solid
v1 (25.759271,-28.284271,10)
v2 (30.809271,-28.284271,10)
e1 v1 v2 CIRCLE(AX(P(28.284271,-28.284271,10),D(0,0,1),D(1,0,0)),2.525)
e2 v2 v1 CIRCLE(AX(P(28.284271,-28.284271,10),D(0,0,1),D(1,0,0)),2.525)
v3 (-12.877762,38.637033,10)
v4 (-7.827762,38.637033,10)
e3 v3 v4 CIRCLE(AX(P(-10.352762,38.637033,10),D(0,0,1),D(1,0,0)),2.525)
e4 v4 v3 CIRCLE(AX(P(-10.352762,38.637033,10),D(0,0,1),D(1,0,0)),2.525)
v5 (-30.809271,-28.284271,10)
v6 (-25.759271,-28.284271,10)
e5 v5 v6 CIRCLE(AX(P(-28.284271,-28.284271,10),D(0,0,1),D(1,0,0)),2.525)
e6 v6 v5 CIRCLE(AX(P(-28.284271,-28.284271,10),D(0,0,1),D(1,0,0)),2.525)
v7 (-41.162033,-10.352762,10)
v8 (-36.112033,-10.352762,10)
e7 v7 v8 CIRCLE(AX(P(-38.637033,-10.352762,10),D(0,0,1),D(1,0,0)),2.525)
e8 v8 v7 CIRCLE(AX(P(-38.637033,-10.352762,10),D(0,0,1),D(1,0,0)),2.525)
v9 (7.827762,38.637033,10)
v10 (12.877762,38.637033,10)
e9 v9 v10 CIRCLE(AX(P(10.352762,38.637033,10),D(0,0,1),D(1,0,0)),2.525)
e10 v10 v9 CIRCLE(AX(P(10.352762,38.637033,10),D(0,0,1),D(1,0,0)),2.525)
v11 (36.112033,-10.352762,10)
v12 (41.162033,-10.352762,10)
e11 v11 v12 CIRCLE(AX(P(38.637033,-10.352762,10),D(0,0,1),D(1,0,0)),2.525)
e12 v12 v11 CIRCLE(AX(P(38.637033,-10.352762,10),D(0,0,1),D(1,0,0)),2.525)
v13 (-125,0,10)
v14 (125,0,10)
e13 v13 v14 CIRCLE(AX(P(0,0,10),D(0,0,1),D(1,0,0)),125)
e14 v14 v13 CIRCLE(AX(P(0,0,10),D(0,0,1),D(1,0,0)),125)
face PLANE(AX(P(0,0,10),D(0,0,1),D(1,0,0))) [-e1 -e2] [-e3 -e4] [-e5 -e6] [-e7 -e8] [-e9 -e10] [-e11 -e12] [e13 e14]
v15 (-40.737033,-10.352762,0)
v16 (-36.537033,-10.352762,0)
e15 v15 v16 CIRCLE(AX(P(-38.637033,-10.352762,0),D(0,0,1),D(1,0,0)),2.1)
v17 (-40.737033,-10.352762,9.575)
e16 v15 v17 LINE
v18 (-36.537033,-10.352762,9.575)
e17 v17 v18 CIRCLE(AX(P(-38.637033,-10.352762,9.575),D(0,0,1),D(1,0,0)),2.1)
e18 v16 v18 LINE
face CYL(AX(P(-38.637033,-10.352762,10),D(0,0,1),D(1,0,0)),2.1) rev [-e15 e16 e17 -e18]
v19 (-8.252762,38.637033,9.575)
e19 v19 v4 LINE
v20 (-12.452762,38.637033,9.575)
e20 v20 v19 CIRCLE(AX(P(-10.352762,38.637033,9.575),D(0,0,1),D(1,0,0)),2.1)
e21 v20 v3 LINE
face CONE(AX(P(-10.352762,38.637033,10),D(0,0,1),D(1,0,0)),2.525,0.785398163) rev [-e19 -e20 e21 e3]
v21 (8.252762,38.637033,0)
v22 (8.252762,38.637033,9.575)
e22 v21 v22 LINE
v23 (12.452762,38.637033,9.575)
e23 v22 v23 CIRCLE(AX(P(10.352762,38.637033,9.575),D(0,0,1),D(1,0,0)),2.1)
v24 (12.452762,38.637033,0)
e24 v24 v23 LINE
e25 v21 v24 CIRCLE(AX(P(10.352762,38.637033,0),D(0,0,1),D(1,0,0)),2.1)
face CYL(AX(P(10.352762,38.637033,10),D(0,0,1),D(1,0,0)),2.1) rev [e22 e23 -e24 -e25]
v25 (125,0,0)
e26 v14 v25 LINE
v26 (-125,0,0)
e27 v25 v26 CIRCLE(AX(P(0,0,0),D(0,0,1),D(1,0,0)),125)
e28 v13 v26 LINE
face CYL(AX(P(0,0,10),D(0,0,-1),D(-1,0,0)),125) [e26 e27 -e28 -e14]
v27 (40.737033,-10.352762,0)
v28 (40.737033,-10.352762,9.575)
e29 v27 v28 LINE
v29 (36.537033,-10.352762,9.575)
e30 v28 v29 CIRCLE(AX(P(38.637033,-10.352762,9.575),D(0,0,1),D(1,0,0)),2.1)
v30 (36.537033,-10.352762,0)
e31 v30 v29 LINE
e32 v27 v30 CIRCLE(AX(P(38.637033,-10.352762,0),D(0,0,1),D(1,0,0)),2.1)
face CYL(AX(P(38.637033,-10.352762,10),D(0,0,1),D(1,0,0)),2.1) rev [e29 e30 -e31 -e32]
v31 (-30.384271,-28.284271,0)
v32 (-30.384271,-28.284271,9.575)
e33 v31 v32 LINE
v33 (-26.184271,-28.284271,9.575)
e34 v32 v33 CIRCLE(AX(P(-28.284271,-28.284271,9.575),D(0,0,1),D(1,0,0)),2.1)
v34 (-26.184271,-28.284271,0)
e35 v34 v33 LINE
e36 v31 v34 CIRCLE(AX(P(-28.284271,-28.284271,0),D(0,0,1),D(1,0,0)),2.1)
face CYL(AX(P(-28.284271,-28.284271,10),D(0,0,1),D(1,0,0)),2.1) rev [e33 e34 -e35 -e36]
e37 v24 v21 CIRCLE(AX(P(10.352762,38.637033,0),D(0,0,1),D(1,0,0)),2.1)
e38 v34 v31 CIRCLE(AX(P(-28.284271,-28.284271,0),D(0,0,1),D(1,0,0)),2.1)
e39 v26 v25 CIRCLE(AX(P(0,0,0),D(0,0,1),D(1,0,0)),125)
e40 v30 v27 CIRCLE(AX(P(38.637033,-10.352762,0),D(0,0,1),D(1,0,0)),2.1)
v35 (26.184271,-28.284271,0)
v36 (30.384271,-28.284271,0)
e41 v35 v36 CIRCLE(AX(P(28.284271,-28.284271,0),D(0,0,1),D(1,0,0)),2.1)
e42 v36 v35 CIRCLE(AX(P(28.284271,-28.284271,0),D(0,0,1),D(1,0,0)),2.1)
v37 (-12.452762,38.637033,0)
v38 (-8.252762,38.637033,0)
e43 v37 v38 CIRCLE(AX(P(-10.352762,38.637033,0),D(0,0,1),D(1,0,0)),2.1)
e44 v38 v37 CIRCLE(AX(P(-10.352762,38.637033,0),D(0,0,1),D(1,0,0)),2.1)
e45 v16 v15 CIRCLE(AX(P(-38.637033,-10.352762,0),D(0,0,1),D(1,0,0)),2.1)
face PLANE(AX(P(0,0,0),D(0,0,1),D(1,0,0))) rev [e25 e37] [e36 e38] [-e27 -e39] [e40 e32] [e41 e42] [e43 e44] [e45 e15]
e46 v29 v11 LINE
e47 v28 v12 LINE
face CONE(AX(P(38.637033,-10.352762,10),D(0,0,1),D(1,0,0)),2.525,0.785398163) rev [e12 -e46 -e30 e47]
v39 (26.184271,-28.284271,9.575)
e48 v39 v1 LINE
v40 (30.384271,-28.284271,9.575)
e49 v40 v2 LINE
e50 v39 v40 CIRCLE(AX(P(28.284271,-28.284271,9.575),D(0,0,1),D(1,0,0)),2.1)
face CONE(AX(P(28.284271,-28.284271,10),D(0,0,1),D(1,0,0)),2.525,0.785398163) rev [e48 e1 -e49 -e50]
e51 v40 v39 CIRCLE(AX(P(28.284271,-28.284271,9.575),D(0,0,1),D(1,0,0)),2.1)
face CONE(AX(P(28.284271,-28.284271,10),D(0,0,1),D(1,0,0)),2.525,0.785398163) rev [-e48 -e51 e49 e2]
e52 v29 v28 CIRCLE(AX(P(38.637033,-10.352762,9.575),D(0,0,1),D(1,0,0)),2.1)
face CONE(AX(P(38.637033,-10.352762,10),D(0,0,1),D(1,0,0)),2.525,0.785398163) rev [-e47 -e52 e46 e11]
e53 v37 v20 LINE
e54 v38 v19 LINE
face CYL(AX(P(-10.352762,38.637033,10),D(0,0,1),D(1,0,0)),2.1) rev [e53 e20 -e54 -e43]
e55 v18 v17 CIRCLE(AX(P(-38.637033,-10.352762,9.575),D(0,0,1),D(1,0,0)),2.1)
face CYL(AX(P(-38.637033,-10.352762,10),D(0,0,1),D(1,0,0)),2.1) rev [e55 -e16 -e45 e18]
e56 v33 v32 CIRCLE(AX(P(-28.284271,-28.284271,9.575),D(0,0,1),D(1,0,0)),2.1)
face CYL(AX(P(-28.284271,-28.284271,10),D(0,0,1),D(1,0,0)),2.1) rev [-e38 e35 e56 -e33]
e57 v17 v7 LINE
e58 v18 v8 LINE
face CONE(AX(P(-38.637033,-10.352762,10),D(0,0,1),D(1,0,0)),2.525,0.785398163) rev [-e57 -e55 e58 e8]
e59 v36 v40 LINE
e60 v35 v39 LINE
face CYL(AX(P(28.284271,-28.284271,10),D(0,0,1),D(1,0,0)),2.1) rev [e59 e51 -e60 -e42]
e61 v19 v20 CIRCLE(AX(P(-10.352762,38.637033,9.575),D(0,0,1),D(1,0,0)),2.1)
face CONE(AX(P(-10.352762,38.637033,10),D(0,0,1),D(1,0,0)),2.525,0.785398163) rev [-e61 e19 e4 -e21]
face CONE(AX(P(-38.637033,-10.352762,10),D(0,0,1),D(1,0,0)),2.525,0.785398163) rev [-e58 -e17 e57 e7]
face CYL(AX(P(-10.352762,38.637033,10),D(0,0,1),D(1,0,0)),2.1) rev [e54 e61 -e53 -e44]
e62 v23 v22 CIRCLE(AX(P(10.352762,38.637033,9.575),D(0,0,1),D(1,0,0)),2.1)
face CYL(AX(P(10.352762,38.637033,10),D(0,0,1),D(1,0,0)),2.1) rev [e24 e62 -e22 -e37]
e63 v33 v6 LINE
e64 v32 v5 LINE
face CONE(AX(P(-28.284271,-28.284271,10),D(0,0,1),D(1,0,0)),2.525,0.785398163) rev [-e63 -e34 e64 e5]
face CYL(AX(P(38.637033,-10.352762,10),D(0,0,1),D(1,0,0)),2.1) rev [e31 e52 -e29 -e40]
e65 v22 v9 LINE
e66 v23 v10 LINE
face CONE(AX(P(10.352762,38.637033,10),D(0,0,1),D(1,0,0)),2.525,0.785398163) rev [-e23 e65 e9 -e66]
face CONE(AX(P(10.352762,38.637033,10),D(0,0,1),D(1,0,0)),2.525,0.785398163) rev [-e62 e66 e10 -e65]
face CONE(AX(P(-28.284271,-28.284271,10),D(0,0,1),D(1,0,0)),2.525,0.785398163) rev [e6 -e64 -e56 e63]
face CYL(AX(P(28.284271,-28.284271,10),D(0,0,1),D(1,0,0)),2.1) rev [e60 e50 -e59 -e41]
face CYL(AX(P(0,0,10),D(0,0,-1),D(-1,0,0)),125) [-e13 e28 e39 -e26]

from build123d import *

# Parameters (mm, degrees)
SKETCH_1_R               = 125
EXTRUDE_1_DEPTH          = 10
M5X0_8_1_AT_2_COUNT      = 2
M5X0_8_1_AT_2_PITCH      = 20.705523608
PATTERN_CIRCULAR_1_COUNT = 3


with BuildPart() as part:
    # 草图1 → 凸台-拉伸1 (new body)
    with BuildSketch(Plane.XY):
        Circle(SKETCH_1_R)
    extrude(amount=EXTRUDE_1_DEPTH)

    # 草图4 → M5x0.8 螺纹孔1 (revolve, cut)
    with BuildSketch(Plane(origin=(10.352761804, 38.637033052, 10), x_dir=(0, -1, 0), z_dir=(1, 0, 0))):
        Polygon((0, 0), (0, 13.6618073), (2.1, 12.4), (2.1, 0.425), (2.525, 0), align=None)
    m5x0_8_1 = revolve(axis=Axis((10.352761804, 38.637033052, 16.35), (0, 0, -1)), mode=Mode.SUBTRACT)

    # M5x0.8 螺纹孔1 at 2: M5x0.8 螺纹孔1 ×2
    with Locations(*[(-i * M5X0_8_1_AT_2_PITCH, 0, 0) for i in range(1, M5X0_8_1_AT_2_COUNT)]):
        add(m5x0_8_1, mode=Mode.SUBTRACT)

    # 阵列(圆周)1: M5x0.8 螺纹孔1 ×3 about axis
    pattern_circular_1_axis = Axis((0, 0, 0), (0, 0, 1))
    for i in range(1, PATTERN_CIRCULAR_1_COUNT):
        add(m5x0_8_1.rotate(pattern_circular_1_axis, i * 360 / PATTERN_CIRCULAR_1_COUNT), mode=Mode.SUBTRACT)

    # 阵列(圆周)1 copy 1 sketch → 阵列(圆周)1 copy 1 (revolve, cut)
    with BuildSketch(Plane(origin=(-28.284271247, -28.284271247, 10), x_dir=(0.8660254037844387, 0.4999999999999998, 0), z_dir=(-0.4999999999999998, 0.8660254037844387, 0))):
        Polygon((0, 0), (0, 13.6618073), (2.1, 12.4), (2.1, 0.425), (2.525, 0), align=None)
    revolve(axis=Axis((-28.284271247, -28.284271247, 16.35), (0, 0, -1)), mode=Mode.SUBTRACT)

    # 阵列(圆周)1 copy 2 sketch → 阵列(圆周)1 copy 2 (revolve, cut)
    with BuildSketch(Plane(origin=(38.637033052, -10.352761804, 10), x_dir=(-0.8660254037844384, 0.5000000000000004, 0), z_dir=(-0.5000000000000004, -0.8660254037844384, 0))):
        Polygon((0, 0), (0, 13.6618073), (2.1, 12.4), (2.1, 0.425), (2.525, 0), align=None)
    revolve(axis=Axis((38.637033052, -10.352761804, 16.35), (0, 0, -1)), mode=Mode.SUBTRACT)


solid = part.part
